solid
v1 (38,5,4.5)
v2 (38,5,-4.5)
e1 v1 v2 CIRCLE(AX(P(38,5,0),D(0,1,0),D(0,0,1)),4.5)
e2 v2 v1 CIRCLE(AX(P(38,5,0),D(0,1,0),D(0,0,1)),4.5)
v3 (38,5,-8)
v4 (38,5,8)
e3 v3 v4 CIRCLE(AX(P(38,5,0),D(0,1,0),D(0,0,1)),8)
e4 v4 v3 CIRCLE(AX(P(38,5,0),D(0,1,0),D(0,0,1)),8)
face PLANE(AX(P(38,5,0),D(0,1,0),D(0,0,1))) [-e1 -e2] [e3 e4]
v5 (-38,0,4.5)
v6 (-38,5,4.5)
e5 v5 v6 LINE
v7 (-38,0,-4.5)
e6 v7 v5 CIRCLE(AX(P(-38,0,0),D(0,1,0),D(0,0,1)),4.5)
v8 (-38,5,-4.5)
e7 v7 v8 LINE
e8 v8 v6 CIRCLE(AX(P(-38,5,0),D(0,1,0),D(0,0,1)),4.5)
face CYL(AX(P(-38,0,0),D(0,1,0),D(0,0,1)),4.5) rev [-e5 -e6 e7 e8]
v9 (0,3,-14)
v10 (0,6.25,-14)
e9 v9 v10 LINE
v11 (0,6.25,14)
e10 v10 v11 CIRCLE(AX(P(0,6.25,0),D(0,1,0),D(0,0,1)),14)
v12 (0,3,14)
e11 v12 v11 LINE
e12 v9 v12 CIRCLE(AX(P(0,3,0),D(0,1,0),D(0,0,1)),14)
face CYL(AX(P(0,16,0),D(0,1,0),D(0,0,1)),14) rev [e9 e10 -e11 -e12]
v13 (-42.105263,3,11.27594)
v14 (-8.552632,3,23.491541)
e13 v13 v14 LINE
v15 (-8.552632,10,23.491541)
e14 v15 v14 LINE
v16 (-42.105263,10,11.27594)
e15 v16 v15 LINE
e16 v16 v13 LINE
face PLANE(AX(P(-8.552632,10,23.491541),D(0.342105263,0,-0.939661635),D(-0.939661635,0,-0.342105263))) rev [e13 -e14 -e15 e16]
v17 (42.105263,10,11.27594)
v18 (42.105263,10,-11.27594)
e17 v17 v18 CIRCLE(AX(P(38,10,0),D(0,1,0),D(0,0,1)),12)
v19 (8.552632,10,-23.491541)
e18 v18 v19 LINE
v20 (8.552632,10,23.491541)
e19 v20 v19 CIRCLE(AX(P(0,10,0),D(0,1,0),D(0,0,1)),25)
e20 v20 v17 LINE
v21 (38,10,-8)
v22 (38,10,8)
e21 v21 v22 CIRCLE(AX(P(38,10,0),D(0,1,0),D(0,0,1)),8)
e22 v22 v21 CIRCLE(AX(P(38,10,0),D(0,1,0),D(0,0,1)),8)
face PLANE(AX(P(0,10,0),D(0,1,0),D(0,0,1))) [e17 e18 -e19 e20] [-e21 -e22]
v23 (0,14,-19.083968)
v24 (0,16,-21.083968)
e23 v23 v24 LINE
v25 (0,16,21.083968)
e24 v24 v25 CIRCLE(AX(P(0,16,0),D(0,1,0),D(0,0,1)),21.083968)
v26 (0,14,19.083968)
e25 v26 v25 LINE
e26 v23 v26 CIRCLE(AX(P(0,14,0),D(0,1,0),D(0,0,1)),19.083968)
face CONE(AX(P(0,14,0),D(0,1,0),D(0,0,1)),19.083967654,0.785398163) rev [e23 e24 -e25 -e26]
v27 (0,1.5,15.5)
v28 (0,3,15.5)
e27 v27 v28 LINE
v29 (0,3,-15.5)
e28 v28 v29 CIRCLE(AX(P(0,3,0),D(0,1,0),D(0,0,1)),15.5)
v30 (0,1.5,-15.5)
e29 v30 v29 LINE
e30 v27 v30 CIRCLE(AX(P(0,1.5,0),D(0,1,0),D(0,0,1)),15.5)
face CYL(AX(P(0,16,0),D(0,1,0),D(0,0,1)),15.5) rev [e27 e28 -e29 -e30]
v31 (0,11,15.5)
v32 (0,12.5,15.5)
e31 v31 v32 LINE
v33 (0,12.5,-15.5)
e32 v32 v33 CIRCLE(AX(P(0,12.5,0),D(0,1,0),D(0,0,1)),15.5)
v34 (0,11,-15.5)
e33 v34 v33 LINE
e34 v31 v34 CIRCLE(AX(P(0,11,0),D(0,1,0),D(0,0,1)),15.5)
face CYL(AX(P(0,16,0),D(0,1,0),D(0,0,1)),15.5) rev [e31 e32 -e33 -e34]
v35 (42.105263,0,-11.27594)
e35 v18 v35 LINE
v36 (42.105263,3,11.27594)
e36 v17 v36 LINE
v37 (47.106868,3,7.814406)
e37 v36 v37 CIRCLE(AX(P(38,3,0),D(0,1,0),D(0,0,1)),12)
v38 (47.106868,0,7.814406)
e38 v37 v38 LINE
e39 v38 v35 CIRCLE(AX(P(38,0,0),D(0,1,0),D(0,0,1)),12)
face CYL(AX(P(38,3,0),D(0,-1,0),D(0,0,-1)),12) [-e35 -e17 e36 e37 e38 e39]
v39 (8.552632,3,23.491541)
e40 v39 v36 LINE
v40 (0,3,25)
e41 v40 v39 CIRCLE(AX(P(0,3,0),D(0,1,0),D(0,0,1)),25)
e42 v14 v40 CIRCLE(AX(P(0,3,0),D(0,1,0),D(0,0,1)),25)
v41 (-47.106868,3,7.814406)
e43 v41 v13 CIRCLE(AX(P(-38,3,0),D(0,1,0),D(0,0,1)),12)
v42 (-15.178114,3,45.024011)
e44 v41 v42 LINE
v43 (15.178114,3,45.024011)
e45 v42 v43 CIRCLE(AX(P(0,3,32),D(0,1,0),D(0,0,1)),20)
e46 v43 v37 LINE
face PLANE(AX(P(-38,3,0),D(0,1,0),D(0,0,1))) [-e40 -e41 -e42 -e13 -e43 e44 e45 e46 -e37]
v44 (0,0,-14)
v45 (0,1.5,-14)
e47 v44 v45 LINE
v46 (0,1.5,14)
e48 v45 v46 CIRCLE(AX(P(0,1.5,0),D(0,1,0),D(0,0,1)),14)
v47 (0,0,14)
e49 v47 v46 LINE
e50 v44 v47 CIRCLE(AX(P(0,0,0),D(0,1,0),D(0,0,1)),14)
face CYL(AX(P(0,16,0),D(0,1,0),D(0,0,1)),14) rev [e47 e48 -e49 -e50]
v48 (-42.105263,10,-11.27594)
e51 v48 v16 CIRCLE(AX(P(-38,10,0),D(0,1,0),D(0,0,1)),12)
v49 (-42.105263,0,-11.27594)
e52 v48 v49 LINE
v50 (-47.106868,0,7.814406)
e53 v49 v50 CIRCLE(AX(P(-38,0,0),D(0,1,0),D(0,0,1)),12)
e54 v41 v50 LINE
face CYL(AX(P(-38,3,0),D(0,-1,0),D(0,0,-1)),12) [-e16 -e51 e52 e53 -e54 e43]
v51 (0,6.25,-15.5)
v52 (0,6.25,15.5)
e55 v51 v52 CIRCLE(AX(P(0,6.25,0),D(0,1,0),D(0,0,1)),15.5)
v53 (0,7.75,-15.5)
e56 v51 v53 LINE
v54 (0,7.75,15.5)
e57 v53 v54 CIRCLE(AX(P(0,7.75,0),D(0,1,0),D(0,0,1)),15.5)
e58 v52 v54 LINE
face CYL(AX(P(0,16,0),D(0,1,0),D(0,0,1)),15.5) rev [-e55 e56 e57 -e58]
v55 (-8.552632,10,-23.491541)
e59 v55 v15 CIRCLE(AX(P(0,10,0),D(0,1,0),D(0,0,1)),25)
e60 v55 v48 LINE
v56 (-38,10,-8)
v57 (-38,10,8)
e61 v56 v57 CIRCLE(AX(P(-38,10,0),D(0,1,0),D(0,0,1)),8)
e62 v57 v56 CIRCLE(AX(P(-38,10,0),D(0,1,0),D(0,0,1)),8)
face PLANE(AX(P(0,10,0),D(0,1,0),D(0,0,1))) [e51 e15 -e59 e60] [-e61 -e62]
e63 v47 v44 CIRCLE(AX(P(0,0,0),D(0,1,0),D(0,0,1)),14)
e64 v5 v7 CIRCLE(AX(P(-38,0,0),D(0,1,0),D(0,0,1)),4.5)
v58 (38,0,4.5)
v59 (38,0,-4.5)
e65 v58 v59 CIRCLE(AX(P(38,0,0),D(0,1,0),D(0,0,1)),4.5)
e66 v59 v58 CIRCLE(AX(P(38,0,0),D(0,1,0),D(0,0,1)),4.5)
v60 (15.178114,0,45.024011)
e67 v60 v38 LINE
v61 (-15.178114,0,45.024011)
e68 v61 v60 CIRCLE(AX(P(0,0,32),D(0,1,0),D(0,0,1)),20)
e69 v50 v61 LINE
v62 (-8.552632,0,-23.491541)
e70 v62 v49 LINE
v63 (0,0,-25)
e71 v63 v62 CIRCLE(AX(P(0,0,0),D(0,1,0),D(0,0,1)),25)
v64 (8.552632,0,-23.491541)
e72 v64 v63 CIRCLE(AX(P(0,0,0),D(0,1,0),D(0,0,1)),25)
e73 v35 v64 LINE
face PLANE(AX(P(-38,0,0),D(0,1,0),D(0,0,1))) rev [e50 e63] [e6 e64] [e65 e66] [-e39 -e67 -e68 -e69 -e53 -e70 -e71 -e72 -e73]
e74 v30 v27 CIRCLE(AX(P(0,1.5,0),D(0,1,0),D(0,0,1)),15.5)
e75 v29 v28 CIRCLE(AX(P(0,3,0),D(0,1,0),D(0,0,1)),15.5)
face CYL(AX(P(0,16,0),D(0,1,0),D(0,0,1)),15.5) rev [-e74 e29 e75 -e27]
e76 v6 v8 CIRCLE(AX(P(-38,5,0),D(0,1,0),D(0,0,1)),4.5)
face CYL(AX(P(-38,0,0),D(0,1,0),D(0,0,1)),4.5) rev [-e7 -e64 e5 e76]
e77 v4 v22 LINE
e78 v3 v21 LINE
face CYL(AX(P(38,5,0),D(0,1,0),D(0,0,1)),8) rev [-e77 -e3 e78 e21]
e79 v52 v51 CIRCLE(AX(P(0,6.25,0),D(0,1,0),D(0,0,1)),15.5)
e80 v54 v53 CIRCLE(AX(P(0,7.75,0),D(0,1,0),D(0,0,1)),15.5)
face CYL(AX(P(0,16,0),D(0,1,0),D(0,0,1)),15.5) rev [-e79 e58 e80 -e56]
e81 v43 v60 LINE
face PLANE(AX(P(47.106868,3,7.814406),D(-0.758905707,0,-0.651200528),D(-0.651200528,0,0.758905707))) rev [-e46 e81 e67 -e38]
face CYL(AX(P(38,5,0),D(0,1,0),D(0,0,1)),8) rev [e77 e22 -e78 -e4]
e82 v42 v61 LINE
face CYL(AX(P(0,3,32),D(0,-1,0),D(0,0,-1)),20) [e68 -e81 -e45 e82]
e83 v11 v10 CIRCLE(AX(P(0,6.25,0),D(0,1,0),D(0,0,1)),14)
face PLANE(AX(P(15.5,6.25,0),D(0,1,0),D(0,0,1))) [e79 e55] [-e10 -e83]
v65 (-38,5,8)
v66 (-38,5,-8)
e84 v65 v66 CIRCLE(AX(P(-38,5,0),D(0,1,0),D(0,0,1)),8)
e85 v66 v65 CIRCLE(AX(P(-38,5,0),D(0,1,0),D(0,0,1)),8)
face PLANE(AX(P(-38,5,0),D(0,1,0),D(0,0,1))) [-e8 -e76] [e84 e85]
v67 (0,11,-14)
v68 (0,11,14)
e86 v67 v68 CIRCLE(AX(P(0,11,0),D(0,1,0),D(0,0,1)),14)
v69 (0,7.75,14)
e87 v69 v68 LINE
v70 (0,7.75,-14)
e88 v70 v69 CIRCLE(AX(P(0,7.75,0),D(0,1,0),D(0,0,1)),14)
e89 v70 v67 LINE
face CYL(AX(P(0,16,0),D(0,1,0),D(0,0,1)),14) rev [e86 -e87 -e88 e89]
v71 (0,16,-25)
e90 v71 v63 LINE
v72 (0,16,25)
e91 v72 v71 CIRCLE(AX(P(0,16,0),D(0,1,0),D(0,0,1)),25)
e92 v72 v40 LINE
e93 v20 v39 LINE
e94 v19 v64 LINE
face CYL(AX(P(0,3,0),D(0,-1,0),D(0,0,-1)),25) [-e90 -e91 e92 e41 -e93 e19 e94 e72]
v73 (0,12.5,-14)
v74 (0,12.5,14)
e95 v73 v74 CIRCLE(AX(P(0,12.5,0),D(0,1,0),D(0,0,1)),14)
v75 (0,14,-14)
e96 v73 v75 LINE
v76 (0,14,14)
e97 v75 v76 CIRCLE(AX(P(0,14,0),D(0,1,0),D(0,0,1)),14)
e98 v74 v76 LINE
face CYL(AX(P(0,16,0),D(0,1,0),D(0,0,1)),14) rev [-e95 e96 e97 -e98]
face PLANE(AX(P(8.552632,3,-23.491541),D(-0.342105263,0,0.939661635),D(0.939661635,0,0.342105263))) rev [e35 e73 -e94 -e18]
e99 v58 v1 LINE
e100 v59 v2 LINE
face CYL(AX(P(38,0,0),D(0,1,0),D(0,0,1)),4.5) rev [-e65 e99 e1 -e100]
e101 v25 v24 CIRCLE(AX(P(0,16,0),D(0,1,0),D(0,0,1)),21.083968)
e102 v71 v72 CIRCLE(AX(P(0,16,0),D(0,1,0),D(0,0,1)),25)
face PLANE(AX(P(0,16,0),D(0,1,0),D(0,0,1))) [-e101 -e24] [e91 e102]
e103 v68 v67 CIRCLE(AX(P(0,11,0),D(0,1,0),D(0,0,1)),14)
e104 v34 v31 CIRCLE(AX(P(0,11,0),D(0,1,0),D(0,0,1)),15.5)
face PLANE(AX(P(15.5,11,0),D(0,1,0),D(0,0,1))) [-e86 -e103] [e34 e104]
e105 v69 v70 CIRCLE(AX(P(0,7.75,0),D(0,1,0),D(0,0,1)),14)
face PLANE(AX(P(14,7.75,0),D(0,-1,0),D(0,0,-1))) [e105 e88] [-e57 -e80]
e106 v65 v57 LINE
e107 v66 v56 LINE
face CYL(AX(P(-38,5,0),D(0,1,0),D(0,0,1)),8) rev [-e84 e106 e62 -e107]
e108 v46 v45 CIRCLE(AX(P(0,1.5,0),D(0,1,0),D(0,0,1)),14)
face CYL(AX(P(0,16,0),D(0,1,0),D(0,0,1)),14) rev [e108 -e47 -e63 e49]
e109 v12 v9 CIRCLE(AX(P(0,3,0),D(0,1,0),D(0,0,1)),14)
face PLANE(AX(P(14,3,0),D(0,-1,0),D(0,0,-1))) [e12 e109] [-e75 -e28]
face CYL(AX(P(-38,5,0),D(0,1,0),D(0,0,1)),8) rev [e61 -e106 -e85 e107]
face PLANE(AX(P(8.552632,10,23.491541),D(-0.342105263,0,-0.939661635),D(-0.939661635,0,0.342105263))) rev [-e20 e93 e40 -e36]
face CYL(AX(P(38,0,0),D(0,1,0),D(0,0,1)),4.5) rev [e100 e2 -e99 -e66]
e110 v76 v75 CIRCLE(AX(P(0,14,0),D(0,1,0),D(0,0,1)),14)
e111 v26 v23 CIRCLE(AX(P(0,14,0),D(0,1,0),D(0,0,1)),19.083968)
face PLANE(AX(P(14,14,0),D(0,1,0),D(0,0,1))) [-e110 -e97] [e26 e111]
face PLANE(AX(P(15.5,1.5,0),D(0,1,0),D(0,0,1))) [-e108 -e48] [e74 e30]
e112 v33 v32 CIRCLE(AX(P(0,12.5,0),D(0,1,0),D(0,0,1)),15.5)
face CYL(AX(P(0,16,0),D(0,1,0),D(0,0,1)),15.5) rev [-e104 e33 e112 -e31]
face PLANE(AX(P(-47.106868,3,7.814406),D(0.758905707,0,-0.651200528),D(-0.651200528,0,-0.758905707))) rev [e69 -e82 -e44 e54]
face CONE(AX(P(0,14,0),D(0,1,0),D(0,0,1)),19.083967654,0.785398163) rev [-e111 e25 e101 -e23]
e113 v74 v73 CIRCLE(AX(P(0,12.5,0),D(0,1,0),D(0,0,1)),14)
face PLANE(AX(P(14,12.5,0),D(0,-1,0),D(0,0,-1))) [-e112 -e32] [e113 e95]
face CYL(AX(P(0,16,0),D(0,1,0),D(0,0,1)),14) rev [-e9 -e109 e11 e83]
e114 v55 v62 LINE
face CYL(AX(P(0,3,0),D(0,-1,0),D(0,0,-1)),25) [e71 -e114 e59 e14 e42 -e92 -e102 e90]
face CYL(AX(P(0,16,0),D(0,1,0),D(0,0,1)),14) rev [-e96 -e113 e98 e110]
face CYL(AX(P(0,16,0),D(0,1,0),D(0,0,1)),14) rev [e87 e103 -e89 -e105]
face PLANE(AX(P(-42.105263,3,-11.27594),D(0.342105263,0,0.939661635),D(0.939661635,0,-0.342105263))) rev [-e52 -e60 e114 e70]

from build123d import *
from build123d.topology import SkipClean

# Parameters (mm, degrees)
BASE_PLATE_DEPTH          = 3
MOUNTING_EARS_DEPTH       = 7
BEARING_HUB_DEPTH         = 13
COUNTERBORE_SKETCH_R      = 8
COUNTERBORES_2X_16_DEPTH  = 5
MOUNTING_HOLE_SKETCH_R    = 4.5
MOUNTING_HOLES_2X_9_DEPTH = 5


with BuildPart() as part:
    # Base Plate Sketch → Base Plate (new body)
    with BuildSketch(Plane(origin=(0, 0, 0), x_dir=(1, 0, 0), z_dir=(0, 1, 0))):
        with BuildLine():
            Line((-42.105263158, 11.275939624), (-8.552631579, 23.491540883))
            ThreePointArc((-8.552631579, 23.491540883), (0, 25), (8.552631579, 23.491540883))
            Line((8.552631579, 23.491540883), (42.105263158, 11.275939624))
            ThreePointArc((42.105263158, 11.275939624), (49.60820541, 3.041310105), (47.10686849, -7.814406331))
            Line((47.10686849, -7.814406331), (15.178114149, -45.024010552))
            ThreePointArc((15.178114149, -45.024010552), (0, -52), (-15.178114149, -45.024010552))
            Line((-15.178114149, -45.024010552), (-47.10686849, -7.814406331))
            ThreePointArc((-47.10686849, -7.814406331), (-49.60820541, 3.041310105), (-42.105263158, 11.275939624))
        make_face()
    extrude(amount=BASE_PLATE_DEPTH)

    # Ear and Hub Profile Sketch → Mounting Ears (add)
    with BuildSketch(Plane(origin=(0, 3, 0), x_dir=(1, 0, 0), z_dir=(0, 1, 0))):
        with BuildLine():
            ThreePointArc((-26, 0), (-31.117527984, -9.830136263), (-42.105263158, -11.275939624))
            Line((-42.105263158, -11.275939624), (-8.552631579, -23.491540883))
            ThreePointArc((-8.552631579, -23.491540883), (-25, 0), (-8.552631579, 23.491540883))
            Line((-8.552631579, 23.491540883), (-42.105263158, 11.275939624))
            ThreePointArc((-42.105263158, 11.275939624), (-31.117527984, 9.830136263), (-26, 0))
        make_face()
        with BuildLine():
            ThreePointArc((-47.10686849, -7.814406331), (-44.829030594, -9.867337085), (-42.105263158, -11.275939624))
            ThreePointArc((-42.105263158, -11.275939624), (-31.117527984, -9.830136263), (-26, 0))
            ThreePointArc((-26, 0), (-31.117527984, 9.830136263), (-42.105263158, 11.275939624))
            ThreePointArc((-42.105263158, 11.275939624), (-49.60820541, 3.041310105), (-47.10686849, -7.814406331))
        make_face()
        with BuildLine():
            ThreePointArc((25, 0), (20.479450548, -14.338483367), (8.552631579, -23.491540883))
            Line((8.552631579, -23.491540883), (42.105263158, -11.275939624))
            ThreePointArc((42.105263158, -11.275939624), (26, 0), (42.105263158, 11.275939624))
            Line((42.105263158, 11.275939624), (8.552631579, 23.491540883))
            ThreePointArc((8.552631579, 23.491540883), (20.479450548, 14.338483367), (25, 0))
        make_face()
        with BuildLine():
            ThreePointArc((42.105263158, 11.275939624), (26, 0), (42.105263158, -11.275939624))
            ThreePointArc((42.105263158, -11.275939624), (44.829030594, -9.867337085), (47.10686849, -7.814406331))
            ThreePointArc((47.10686849, -7.814406331), (49.25349772, -4.166388011), (50, 0))
            ThreePointArc((50, 0), (47.830136263, 6.882472016), (42.105263158, 11.275939624))
        make_face()
    extrude(amount=MOUNTING_EARS_DEPTH)

    # Sketch2_5 → Bearing Hub (add)
    with SkipClean():  # the faces are left unmerged after this step: merging them gives an invalid solid
        with BuildSketch(Plane(origin=(0, 3, 0), x_dir=(1, 0, 0), z_dir=(0, 1, 0))):
            with BuildLine():
                ThreePointArc((-8.552631579, 23.491540883), (-25, 0), (-8.552631579, -23.491540883))
                ThreePointArc((-8.552631579, -23.491540883), (0, -25), (8.552631579, -23.491540883))
                ThreePointArc((8.552631579, -23.491540883), (20.479450548, -14.338483367), (25, 0))
                ThreePointArc((25, 0), (20.479450548, 14.338483367), (8.552631579, 23.491540883))
                ThreePointArc((8.552631579, 23.491540883), (0, 25), (-8.552631579, 23.491540883))
            make_face()
        extrude(amount=BEARING_HUB_DEPTH)

    # Bearing Bore Profile Sketch → Bearing Bore (revolve, cut)
    with SkipClean():  # the faces are left unmerged after this step: merging them gives an invalid solid
        with BuildSketch(Plane.XY, mode=Mode.PRIVATE) as bearing_bore_sk:
            Polygon((21.083967654, 16), (0, 16), (0, 0), (14, 0), (14, 1.5), (15.5, 1.5), (15.5, 3), (14, 3), (14, 6.25), (15.5, 6.25), (15.5, 7.75), (14, 7.75), (14, 11), (15.5, 11), (15.5, 12.5), (14, 12.5), (14, 14), (19.083967654, 14), align=None)
        revolve(bearing_bore_sk.sketch.rotate(Axis((0, 16, 0), (0, -1, 0)), 90), axis=Axis((0, 16, 0), (0, -1, 0)), mode=Mode.SUBTRACT)

    # Counterbore Sketch → Counterbores 2x_16 (cut)
    with SkipClean():  # the faces are left unmerged after this step: merging them gives an invalid solid
        with BuildSketch(Plane(origin=(0, 10, 0), x_dir=(1, 0, 0), z_dir=(0, 1, 0))):
            with Locations(Location((38, 0, 0), (0, 0, 270))):
                Circle(COUNTERBORE_SKETCH_R)
            with Locations(Location((-38, 0, 0), (0, 0, 270))):
                Circle(COUNTERBORE_SKETCH_R)
        extrude(amount=-COUNTERBORES_2X_16_DEPTH, mode=Mode.SUBTRACT)

    # Mounting Hole Sketch → Mounting Holes 2x_9 (cut)
    with SkipClean():  # the faces are left unmerged after this step: merging them gives an invalid solid
        with BuildSketch(Plane(origin=(0, 5, 0), x_dir=(1, 0, 0), z_dir=(0, 1, 0))):
            with Locations(Location((38, 0, 0), (0, 0, 270))):
                Circle(MOUNTING_HOLE_SKETCH_R)
            with Locations(Location((-38, 0, 0), (0, 0, 270))):
                Circle(MOUNTING_HOLE_SKETCH_R)
        extrude(amount=-MOUNTING_HOLES_2X_9_DEPTH, mode=Mode.SUBTRACT)


solid = part.part
